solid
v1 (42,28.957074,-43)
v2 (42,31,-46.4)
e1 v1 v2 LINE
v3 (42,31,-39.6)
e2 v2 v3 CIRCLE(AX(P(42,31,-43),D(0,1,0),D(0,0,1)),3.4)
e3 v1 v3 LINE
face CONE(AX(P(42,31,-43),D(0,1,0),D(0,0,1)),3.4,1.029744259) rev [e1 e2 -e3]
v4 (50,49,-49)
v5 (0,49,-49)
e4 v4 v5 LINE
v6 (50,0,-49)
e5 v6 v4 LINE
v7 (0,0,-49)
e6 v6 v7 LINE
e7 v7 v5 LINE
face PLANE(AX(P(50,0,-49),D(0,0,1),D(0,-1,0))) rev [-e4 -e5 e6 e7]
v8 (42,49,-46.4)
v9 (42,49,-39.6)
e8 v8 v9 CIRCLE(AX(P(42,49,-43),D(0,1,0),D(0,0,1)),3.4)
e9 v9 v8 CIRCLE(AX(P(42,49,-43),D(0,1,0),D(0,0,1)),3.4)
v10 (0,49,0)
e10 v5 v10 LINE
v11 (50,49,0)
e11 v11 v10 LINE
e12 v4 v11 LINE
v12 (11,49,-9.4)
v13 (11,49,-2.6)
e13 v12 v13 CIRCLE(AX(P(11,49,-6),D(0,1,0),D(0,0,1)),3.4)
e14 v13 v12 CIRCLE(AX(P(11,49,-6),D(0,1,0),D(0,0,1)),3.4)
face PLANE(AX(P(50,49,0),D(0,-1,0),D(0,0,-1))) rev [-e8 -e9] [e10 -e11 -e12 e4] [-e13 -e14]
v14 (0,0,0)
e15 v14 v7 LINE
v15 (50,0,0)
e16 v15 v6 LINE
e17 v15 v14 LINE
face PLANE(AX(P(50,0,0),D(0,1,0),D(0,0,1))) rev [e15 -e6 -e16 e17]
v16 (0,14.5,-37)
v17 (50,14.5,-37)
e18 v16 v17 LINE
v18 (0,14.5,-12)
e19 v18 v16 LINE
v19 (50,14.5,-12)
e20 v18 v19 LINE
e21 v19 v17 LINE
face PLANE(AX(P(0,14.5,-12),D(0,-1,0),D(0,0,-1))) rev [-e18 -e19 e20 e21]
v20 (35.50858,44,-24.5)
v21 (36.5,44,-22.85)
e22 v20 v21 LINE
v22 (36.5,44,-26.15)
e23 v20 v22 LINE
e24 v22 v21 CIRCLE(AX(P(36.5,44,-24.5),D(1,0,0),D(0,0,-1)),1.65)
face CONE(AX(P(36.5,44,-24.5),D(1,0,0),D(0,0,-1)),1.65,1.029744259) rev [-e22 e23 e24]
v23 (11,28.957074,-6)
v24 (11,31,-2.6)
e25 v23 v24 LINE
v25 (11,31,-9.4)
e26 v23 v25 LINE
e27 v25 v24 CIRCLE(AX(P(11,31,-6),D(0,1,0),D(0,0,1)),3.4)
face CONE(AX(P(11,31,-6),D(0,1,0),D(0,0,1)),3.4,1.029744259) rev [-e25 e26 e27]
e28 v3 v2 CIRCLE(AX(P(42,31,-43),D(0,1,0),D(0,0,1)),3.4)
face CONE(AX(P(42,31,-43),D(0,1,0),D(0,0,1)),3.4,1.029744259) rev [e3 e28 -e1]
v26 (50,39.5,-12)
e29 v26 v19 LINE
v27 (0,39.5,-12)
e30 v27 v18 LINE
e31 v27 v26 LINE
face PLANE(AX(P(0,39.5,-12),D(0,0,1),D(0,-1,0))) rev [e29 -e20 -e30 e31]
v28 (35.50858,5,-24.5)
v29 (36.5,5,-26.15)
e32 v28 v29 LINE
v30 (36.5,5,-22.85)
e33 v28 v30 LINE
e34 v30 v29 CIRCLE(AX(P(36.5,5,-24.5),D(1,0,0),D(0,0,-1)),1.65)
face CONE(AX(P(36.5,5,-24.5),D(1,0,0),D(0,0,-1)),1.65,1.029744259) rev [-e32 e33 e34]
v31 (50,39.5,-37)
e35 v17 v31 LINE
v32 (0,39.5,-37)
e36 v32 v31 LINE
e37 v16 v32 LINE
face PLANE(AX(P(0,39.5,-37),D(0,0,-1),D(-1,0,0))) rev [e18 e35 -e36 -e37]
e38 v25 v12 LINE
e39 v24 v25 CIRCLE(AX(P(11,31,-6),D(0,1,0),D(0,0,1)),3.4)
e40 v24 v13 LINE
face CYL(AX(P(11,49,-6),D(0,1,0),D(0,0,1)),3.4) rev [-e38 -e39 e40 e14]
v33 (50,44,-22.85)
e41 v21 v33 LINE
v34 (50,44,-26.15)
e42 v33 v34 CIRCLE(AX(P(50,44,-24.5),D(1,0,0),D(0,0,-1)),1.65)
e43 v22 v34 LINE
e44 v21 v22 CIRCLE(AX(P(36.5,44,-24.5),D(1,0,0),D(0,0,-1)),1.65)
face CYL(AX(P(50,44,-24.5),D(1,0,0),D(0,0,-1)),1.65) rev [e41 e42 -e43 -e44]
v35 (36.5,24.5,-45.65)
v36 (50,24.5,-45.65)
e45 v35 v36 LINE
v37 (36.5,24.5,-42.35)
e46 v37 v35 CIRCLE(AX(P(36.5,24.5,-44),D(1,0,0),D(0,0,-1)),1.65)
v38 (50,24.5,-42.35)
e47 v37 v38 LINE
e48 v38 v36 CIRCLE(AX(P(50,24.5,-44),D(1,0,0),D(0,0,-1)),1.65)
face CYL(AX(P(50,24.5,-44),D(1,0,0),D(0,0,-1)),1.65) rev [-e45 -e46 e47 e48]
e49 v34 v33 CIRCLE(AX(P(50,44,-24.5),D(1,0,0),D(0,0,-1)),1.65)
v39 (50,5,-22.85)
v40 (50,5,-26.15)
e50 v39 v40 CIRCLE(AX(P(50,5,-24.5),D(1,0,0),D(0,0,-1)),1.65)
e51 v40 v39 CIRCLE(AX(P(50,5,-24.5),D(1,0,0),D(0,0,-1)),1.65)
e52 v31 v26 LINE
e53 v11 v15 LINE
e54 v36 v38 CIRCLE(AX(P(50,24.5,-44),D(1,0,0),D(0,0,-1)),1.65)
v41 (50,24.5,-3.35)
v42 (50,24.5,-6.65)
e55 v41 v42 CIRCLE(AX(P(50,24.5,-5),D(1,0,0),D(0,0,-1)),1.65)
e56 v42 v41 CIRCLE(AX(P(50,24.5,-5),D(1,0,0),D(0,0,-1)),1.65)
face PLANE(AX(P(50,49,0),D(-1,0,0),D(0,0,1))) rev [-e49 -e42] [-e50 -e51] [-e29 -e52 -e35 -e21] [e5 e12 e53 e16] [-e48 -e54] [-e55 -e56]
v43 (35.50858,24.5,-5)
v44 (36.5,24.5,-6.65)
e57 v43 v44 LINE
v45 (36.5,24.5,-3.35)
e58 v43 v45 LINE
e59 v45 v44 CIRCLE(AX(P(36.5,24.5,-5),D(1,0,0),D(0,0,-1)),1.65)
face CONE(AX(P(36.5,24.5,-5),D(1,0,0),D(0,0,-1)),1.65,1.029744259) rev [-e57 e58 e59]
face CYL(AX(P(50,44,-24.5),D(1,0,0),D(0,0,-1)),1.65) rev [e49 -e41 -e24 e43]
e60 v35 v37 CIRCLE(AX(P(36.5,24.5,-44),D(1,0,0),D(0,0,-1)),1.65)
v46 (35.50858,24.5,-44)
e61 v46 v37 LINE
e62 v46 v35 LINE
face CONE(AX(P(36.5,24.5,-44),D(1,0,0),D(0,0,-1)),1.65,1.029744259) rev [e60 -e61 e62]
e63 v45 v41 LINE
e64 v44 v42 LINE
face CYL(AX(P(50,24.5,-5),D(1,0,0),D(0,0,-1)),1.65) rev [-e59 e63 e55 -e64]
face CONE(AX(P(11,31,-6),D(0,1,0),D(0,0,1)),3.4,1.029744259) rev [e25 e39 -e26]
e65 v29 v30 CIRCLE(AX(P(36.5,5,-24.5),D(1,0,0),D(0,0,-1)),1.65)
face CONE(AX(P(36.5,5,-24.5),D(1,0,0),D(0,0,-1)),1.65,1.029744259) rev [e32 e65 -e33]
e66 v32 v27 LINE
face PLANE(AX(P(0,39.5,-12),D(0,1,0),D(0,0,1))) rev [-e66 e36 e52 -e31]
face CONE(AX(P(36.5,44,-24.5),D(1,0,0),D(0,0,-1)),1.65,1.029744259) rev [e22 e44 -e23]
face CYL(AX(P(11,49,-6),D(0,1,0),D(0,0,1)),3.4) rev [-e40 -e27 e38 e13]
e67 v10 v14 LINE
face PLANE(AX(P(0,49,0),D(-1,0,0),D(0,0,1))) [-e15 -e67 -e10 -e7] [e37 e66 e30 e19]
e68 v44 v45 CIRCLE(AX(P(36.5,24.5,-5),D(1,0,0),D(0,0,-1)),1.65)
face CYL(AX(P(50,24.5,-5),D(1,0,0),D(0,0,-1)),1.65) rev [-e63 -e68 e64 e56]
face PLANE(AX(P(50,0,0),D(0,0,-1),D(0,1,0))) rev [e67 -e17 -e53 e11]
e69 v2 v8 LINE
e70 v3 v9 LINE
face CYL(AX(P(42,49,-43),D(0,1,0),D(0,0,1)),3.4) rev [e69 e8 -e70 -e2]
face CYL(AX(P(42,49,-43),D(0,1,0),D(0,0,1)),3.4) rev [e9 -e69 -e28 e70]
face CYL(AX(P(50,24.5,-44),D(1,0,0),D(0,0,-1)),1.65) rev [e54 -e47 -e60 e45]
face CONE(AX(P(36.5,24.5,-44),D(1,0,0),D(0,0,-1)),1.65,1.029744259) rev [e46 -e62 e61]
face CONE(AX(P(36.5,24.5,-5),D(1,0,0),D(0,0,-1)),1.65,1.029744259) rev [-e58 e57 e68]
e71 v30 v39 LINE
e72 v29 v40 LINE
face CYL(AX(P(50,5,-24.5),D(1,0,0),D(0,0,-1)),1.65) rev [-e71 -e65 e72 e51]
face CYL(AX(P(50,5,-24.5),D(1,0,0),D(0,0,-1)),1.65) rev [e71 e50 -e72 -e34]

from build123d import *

# Parameters (mm, degrees)
SKETCH_2_W             = 49
SKETCH_2_H             = 49
EXTRUDE_2_DEPTH        = 50
SKETCH_3_W             = 25
SKETCH_3_H             = 25
CUT_EXTRUDE_1_DEPTH    = 50
HOLE_WIZARD_M4_1_D     = 3.3
HOLE_WIZARD_M4_1_DEPTH = 13.5
HOLE_WIZARD_M4_1_TIP   = 0.991420021
HOLE_WIZARD_M8_1_D     = 6.8
HOLE_WIZARD_M8_1_DEPTH = 18
HOLE_WIZARD_M8_1_TIP   = 2.042926105


with BuildPart() as part:
    # 草图2 → 凸台-拉伸2 (new body)
    with BuildSketch(Plane(origin=(0, 0, 0), x_dir=(0, 0, -1), z_dir=(1, 0, 0))):
        with Locations((24.5, 24.5)):
            Rectangle(SKETCH_2_W, SKETCH_2_H)
    extrude(amount=EXTRUDE_2_DEPTH)

    # 草图3 → 切除-拉伸1 (cut)
    with BuildSketch(Plane(origin=(50, 0, 0), x_dir=(0, 0, -1), z_dir=(1, 0, 0))):
        with Locations((24.5, 27)):
            Rectangle(SKETCH_3_W, SKETCH_3_H)
    extrude(amount=-CUT_EXTRUDE_1_DEPTH, mode=Mode.SUBTRACT)

    # M4 螺纹孔1
    with Locations(Plane(origin=(50, 0, 0), x_dir=(0, 0, -1), z_dir=(1, 0, 0))):
        with Locations((24.5, 44), (5, 24.5), (24.5, 5), (44, 24.5)):
            Hole(HOLE_WIZARD_M4_1_D / 2, depth=HOLE_WIZARD_M4_1_DEPTH)
            with Locations((0, 0, -(HOLE_WIZARD_M4_1_DEPTH + HOLE_WIZARD_M4_1_TIP / 2))):  # 118° drill point
                Cone(0, HOLE_WIZARD_M4_1_D / 2, HOLE_WIZARD_M4_1_TIP, mode=Mode.SUBTRACT)

    # M8 螺纹孔1
    with Locations(Plane(origin=(0, 49, 0), x_dir=(-1, 0, 0), z_dir=(0, 1, 0))):
        with Locations((-11, -6), (-42, -43)):
            Hole(HOLE_WIZARD_M8_1_D / 2, depth=HOLE_WIZARD_M8_1_DEPTH)
            with Locations((0, 0, -(HOLE_WIZARD_M8_1_DEPTH + HOLE_WIZARD_M8_1_TIP / 2))):  # 118° drill point
                Cone(0, HOLE_WIZARD_M8_1_D / 2, HOLE_WIZARD_M8_1_TIP, mode=Mode.SUBTRACT)


solid = part.part
